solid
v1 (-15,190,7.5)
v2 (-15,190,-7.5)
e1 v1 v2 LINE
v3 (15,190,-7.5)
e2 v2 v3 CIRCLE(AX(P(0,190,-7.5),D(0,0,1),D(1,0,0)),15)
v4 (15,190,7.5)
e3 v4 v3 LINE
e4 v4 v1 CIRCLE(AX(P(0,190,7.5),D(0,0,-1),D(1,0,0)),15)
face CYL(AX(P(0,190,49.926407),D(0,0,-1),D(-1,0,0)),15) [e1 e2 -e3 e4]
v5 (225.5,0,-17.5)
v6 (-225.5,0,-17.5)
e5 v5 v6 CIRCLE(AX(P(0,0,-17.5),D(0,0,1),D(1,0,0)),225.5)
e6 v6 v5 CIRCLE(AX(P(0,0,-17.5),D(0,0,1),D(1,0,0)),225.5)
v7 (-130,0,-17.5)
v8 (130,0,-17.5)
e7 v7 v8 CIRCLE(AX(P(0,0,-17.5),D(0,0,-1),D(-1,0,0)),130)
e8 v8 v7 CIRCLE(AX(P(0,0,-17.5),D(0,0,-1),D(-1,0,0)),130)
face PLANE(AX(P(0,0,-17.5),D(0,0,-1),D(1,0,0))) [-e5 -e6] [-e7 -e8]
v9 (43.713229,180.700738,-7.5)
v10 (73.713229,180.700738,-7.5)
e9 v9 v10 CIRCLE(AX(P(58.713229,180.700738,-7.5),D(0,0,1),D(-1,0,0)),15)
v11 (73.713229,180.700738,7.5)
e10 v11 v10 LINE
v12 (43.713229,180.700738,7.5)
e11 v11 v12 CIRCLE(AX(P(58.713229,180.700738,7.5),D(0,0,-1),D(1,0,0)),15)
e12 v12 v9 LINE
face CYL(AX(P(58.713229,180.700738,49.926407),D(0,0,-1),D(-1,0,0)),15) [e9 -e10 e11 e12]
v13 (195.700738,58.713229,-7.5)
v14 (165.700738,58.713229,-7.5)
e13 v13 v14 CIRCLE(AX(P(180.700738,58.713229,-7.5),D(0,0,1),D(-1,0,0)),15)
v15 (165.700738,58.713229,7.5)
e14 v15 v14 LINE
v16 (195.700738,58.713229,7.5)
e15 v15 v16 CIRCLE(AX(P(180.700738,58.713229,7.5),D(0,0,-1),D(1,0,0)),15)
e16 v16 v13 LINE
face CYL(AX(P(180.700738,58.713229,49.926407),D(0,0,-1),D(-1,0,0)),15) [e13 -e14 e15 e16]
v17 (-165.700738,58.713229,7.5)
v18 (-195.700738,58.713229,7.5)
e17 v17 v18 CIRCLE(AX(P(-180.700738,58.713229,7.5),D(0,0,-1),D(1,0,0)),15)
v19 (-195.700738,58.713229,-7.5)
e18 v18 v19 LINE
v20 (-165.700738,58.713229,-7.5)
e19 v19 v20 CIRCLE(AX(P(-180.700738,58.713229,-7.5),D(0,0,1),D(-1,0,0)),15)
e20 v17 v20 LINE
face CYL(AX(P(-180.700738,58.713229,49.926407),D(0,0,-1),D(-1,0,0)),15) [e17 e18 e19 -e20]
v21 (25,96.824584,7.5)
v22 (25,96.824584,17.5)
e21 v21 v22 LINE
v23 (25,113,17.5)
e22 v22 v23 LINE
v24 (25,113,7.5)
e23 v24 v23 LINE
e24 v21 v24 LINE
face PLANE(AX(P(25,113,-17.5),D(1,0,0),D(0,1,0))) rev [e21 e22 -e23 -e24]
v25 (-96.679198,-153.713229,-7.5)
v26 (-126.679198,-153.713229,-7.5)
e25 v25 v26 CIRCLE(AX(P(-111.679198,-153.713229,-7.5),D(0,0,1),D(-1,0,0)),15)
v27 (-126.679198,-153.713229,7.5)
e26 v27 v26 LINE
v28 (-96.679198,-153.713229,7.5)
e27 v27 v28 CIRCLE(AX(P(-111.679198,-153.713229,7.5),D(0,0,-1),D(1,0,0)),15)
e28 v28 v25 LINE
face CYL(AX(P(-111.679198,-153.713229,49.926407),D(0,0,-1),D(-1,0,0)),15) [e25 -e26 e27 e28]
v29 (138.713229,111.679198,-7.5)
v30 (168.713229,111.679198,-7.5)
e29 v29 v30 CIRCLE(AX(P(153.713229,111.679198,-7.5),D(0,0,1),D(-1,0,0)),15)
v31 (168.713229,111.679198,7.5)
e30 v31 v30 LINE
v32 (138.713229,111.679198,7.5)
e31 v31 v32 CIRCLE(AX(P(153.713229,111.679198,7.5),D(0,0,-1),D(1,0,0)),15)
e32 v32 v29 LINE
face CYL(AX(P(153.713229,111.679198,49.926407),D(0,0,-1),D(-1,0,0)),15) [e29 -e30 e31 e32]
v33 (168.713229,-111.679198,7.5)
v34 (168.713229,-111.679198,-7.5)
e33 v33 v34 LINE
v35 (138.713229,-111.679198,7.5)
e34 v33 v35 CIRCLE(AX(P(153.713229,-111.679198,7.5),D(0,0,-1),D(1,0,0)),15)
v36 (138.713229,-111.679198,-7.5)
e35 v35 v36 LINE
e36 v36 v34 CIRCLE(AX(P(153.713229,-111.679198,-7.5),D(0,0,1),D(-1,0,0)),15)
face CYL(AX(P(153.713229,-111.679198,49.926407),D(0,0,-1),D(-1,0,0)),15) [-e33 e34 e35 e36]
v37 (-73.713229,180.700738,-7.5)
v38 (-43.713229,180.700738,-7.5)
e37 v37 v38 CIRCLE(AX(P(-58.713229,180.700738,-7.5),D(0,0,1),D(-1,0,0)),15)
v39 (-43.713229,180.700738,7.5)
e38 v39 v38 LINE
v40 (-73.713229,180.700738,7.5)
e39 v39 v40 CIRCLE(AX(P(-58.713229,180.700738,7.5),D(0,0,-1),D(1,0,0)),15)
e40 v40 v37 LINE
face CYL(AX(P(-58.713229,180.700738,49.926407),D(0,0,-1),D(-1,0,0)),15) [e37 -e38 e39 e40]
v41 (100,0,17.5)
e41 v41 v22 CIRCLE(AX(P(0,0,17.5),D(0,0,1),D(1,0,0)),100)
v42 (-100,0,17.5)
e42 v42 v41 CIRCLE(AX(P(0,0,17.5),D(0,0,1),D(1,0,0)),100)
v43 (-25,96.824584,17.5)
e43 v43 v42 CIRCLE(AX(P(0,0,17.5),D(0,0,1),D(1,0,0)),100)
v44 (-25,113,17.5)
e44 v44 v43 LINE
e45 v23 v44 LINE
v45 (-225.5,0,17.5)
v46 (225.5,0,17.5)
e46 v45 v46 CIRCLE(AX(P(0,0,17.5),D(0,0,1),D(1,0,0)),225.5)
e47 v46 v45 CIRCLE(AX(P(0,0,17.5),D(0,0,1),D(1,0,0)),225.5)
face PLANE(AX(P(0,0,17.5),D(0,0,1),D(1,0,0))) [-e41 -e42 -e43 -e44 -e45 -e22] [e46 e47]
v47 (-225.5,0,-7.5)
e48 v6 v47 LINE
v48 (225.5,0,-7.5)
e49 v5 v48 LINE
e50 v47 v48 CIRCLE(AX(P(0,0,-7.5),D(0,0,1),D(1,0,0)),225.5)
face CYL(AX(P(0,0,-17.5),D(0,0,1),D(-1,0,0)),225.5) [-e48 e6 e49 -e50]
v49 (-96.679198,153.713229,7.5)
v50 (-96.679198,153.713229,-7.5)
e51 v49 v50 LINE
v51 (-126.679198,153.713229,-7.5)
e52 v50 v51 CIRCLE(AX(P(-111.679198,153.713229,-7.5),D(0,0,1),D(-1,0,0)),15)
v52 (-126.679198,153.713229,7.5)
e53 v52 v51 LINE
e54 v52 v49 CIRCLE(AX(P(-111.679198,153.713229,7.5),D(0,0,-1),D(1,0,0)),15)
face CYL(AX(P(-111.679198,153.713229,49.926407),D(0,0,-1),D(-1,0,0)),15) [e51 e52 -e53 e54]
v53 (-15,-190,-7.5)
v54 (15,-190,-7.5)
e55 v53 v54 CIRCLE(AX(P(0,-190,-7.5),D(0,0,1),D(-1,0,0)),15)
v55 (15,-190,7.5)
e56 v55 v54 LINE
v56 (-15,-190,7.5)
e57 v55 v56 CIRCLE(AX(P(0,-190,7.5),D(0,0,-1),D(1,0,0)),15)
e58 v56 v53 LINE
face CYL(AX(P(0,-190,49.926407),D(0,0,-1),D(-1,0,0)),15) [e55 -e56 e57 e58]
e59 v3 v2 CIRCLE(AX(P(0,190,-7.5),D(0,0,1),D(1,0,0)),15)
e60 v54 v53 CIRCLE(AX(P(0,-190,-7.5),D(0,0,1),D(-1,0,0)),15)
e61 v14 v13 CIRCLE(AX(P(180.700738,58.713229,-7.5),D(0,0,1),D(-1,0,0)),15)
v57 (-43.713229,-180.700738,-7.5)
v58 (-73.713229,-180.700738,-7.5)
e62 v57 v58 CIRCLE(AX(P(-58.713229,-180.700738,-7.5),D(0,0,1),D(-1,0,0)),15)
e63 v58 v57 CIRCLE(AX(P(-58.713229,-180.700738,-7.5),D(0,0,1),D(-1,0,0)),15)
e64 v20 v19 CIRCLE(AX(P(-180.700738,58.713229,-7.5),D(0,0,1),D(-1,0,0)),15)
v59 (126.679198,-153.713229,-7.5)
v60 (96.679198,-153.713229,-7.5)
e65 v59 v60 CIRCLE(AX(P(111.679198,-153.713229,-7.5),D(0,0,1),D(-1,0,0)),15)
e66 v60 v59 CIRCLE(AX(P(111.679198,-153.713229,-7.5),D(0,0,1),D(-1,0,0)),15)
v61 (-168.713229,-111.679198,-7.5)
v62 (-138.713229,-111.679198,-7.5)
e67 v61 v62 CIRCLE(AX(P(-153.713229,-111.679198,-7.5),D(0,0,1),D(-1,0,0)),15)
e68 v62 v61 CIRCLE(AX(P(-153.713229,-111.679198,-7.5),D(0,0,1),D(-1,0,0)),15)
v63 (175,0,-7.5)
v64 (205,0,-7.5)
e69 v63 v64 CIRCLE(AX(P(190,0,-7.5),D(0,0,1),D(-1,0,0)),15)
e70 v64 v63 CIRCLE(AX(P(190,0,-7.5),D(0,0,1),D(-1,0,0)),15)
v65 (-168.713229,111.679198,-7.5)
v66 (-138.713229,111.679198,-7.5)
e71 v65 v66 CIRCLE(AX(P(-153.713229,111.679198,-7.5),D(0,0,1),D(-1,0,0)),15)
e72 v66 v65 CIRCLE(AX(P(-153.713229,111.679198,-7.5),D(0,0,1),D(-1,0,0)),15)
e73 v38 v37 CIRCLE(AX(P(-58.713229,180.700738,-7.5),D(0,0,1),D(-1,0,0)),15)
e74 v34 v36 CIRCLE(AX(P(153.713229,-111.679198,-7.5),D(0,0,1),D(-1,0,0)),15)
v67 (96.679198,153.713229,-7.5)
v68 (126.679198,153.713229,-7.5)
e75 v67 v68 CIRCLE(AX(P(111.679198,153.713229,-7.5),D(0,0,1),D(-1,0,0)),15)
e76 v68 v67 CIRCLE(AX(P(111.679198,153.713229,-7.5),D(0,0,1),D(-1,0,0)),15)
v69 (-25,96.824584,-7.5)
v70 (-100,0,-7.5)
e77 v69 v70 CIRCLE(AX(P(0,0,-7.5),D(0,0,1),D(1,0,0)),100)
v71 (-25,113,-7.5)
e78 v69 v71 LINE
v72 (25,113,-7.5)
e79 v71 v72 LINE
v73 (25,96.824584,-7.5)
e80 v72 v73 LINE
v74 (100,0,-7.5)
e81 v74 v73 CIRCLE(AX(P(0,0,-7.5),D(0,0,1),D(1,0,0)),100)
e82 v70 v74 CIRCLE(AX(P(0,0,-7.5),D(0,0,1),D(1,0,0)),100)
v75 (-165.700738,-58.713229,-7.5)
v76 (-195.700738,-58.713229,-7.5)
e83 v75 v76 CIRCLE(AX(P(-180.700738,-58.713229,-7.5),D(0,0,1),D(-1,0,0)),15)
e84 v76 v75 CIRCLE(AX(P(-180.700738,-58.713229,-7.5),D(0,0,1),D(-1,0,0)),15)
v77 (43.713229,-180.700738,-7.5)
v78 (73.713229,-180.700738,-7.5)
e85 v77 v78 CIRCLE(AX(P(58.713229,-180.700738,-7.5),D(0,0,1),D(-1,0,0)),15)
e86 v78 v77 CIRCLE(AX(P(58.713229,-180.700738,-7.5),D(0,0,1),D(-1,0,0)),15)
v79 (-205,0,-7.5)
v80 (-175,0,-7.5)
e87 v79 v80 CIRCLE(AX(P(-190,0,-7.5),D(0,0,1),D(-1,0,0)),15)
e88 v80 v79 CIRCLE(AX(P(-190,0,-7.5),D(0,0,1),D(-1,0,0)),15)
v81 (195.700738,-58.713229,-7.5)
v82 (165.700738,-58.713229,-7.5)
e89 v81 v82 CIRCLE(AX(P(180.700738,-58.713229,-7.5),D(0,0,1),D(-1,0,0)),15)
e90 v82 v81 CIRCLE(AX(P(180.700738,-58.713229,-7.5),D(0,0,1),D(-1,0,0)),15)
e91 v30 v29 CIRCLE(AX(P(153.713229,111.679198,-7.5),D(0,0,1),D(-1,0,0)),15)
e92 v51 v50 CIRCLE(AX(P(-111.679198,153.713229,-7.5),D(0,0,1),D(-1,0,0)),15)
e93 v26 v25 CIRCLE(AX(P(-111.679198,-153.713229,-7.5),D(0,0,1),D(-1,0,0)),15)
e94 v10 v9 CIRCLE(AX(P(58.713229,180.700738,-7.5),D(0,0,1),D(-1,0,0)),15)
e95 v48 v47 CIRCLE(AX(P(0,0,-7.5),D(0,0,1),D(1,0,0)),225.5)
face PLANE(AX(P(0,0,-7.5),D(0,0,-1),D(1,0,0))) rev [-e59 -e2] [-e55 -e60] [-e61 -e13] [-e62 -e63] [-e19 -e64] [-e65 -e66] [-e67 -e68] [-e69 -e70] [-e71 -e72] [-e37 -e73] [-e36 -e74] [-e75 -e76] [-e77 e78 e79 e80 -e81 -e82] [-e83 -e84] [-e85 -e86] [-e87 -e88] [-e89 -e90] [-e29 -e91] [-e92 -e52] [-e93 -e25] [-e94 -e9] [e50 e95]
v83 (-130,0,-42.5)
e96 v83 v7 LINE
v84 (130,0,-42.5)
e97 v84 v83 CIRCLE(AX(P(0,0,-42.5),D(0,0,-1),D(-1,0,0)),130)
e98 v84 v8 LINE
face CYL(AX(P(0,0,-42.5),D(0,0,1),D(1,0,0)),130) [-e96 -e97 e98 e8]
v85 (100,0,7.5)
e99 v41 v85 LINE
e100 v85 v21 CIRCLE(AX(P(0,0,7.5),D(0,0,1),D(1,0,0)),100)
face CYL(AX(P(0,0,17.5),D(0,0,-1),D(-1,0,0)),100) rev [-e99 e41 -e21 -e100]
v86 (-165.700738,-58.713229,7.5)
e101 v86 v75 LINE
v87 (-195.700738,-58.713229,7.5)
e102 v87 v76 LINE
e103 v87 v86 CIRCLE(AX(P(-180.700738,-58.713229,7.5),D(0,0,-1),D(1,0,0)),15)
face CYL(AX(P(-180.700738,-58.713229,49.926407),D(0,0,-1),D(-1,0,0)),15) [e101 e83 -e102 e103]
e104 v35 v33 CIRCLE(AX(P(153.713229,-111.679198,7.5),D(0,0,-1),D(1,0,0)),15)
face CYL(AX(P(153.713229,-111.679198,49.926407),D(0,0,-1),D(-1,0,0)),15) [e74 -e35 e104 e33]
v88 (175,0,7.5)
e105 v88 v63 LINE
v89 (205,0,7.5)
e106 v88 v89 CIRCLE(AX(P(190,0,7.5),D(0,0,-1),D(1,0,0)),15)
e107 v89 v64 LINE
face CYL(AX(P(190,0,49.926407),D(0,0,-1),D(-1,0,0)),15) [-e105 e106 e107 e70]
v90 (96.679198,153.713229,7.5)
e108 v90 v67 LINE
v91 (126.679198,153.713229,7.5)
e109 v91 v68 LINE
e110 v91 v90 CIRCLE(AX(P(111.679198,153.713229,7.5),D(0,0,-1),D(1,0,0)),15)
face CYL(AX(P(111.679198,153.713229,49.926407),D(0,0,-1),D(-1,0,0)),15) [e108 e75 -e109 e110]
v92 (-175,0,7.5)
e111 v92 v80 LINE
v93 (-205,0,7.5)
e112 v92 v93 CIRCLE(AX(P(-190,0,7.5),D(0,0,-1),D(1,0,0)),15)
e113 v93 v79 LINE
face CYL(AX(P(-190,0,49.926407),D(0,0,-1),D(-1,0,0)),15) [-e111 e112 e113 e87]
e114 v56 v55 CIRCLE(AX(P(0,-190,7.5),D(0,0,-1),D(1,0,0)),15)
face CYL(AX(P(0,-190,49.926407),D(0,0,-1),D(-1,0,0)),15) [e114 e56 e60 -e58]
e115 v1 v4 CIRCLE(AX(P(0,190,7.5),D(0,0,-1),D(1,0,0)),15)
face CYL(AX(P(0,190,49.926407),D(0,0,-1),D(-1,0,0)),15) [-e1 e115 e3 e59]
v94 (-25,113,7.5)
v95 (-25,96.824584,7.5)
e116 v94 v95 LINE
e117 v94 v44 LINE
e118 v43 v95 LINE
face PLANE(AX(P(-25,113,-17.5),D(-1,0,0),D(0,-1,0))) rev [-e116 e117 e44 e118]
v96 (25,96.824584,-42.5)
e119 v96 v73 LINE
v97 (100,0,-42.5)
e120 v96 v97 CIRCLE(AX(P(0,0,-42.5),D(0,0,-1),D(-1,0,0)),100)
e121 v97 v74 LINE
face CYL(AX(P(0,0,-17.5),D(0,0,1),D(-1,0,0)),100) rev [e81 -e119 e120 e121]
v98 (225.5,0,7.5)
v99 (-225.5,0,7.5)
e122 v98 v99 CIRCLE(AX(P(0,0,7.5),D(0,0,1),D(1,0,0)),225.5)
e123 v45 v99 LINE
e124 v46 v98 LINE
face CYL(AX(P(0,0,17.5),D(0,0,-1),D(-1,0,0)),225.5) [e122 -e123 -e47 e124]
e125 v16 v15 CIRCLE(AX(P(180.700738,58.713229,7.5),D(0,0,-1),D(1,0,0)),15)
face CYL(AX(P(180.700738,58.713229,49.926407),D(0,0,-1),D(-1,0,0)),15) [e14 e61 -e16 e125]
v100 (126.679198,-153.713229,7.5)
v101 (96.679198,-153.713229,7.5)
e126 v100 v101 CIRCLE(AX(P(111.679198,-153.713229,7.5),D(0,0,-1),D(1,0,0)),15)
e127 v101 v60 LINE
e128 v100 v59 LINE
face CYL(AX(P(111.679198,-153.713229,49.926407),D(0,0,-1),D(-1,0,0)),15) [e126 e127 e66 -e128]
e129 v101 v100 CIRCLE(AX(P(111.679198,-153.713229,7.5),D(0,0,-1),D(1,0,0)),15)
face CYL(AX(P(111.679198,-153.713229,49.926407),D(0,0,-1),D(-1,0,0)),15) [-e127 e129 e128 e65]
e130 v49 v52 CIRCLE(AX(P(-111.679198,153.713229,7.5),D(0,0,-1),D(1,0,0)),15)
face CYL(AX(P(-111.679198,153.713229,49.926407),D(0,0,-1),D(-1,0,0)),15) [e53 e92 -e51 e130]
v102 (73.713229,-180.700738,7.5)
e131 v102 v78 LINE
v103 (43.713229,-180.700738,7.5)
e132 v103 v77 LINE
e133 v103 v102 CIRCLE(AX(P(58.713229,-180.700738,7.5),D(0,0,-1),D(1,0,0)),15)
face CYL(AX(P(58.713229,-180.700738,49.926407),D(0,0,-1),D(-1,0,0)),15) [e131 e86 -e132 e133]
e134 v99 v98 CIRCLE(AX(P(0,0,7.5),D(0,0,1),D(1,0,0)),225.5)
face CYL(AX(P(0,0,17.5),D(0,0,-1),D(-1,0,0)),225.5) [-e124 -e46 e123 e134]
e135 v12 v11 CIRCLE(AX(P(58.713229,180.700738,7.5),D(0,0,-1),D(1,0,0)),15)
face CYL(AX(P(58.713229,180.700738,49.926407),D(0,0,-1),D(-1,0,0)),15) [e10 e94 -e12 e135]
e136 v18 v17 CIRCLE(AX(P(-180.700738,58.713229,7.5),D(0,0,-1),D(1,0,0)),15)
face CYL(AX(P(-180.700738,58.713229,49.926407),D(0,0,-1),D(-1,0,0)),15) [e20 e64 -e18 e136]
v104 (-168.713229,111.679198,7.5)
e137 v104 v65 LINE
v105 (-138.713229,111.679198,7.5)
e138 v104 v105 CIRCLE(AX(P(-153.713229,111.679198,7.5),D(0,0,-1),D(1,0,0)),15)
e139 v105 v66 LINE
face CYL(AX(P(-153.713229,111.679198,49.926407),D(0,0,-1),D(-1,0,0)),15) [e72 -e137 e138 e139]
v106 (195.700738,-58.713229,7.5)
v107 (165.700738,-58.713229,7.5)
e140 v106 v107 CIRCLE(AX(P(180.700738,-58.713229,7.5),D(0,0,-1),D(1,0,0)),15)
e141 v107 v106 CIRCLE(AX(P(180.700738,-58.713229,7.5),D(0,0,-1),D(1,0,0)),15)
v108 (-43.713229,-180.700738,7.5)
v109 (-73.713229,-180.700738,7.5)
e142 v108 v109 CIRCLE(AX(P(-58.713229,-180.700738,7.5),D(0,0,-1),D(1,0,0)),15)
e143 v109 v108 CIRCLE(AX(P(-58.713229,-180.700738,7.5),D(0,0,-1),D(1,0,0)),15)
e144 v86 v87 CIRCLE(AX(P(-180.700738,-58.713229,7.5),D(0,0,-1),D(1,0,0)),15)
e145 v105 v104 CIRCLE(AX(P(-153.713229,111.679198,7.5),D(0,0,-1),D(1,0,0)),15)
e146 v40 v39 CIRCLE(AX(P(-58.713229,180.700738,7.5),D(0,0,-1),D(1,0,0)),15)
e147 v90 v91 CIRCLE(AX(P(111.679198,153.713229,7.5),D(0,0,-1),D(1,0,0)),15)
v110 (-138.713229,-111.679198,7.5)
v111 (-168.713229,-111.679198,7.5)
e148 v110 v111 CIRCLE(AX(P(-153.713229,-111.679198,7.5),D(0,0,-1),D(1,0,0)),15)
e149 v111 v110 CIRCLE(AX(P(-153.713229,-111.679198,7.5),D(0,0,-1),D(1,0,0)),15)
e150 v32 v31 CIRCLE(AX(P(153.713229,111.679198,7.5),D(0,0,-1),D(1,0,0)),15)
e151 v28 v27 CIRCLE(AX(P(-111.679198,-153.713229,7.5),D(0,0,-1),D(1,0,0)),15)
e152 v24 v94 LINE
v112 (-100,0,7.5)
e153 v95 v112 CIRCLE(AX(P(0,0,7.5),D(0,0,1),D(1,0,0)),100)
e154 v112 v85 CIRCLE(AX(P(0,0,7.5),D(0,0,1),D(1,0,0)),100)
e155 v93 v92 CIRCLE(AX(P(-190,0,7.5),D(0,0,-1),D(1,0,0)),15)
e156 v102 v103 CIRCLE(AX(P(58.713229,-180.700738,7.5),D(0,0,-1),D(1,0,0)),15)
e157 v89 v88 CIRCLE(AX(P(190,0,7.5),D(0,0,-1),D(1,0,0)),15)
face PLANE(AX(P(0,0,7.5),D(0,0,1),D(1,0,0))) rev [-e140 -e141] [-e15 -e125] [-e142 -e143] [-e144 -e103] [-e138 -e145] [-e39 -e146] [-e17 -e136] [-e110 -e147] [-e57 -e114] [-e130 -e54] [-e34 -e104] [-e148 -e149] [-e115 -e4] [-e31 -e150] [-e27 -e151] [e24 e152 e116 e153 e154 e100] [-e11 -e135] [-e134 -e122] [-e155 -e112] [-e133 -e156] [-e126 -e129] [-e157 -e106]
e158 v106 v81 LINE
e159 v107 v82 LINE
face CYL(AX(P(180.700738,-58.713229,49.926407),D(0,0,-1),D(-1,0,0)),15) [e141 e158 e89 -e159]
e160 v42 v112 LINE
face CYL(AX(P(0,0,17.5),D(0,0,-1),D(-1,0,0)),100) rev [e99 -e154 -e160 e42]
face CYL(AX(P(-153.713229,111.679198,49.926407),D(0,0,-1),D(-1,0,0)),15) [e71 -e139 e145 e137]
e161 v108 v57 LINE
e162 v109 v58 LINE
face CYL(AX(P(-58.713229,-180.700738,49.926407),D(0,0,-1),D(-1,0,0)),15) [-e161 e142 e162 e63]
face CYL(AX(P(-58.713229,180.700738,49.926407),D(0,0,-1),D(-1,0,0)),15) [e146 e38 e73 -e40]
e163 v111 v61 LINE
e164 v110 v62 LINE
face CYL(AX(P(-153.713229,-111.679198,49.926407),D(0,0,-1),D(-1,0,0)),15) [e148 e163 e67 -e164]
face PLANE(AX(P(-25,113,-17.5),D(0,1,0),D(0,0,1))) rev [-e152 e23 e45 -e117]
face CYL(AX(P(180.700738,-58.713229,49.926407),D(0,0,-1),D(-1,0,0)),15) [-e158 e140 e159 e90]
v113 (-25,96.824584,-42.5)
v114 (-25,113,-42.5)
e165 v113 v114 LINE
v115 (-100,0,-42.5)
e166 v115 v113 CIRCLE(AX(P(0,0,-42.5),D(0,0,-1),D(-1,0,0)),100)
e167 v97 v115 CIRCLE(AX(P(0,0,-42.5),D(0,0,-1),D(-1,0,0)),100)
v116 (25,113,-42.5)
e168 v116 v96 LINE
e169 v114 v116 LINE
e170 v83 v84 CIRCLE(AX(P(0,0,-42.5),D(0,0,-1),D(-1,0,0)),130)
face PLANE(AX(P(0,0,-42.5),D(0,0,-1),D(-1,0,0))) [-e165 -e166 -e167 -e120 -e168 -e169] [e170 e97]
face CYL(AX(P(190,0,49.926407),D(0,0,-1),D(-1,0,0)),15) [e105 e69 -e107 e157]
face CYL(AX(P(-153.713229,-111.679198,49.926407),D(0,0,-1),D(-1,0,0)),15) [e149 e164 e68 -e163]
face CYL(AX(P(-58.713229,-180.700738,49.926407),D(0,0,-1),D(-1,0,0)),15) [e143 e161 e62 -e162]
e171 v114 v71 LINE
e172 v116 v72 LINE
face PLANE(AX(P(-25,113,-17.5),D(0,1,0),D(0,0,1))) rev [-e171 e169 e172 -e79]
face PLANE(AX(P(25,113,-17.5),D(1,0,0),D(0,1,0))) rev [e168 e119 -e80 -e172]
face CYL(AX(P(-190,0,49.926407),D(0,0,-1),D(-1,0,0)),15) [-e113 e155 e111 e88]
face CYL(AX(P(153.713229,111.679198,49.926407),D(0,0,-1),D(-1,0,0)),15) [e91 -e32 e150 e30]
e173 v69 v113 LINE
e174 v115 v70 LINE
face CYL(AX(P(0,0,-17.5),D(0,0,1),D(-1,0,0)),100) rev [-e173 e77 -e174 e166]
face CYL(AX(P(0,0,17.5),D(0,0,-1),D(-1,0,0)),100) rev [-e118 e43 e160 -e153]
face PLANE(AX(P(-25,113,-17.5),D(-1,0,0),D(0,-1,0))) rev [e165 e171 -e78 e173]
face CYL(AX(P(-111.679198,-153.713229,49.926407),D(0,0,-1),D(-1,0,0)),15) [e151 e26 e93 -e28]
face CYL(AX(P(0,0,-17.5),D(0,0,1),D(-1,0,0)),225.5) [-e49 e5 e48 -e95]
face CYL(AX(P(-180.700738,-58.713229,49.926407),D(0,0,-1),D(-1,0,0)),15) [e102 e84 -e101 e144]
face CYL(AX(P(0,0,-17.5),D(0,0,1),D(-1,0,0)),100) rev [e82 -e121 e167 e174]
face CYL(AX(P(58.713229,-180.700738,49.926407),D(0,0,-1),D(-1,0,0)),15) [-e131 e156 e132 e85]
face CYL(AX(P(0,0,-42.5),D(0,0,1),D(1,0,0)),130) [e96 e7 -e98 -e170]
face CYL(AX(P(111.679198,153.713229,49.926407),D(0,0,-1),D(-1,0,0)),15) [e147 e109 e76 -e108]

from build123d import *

# Parameters (mm, degrees)
BOSS_EXTRUDE1_START = 7.5
SKETCH1_R           = 225.5
SKETCH1_R_2         = 100
BOSS_EXTRUDE1_DEPTH = 10
SKETCH2_R           = 15
BOSS_EXTRUDE2_DEPTH = 15
SKETCH3_W           = 50
SKETCH3_H           = 48.595629982
CUT_EXTRUDE1_DEPTH  = 321.820043015
SKETCH4_R           = 130
BOSS_EXTRUDE3_DEPTH = 25


with BuildPart() as part:
    # Sketch1 → Boss-Extrude1 (new body)
    with BuildSketch(Plane.XY.offset(BOSS_EXTRUDE1_START)):
        Circle(SKETCH1_R)
        Circle(SKETCH1_R_2, mode=Mode.SUBTRACT)
    extrude(amount=BOSS_EXTRUDE1_DEPTH)


with BuildPart() as body_2:
    # Mirror1: mirrored copy
    add(part.part.mirror(Plane.XY))


with BuildPart() as part_1:
    add(part.part)

    add(body_2.part)  # Boss-Extrude2 merges body 2
    # Sketch2 → Boss-Extrude2 (add)
    with BuildSketch(Plane.XY.offset(-7.5)):
        with Locations((0, 190)):
            Circle(SKETCH2_R)
        with Locations(Location((58.713228931, 180.700738096, 0), (0, 0, 180))):
            Circle(SKETCH2_R)
        with Locations(Location((111.679197936, 153.713228931, 0), (0, 0, 180))):
            Circle(SKETCH2_R)
        with Locations(Location((153.713228931, 111.679197936, 0), (0, 0, 180))):
            Circle(SKETCH2_R)
        with Locations(Location((180.700738096, 58.713228931, 0), (0, 0, 180))):
            Circle(SKETCH2_R)
        with Locations(Location((190, 0, 0), (0, 0, 180))):
            Circle(SKETCH2_R)
        with Locations(Location((180.700738096, -58.713228931, 0), (0, 0, 180))):
            Circle(SKETCH2_R)
        with Locations(Location((153.713228931, -111.679197936, 0), (0, 0, 180))):
            Circle(SKETCH2_R)
        with Locations(Location((111.679197936, -153.713228931, 0), (0, 0, 180))):
            Circle(SKETCH2_R)
        with Locations(Location((58.713228931, -180.700738096, 0), (0, 0, 180))):
            Circle(SKETCH2_R)
        with Locations(Location((0, -190, 0), (0, 0, 180))):
            Circle(SKETCH2_R)
        with Locations(Location((-58.713228931, -180.700738096, 0), (0, 0, 180))):
            Circle(SKETCH2_R)
        with Locations(Location((-111.679197936, -153.713228931, 0), (0, 0, 180))):
            Circle(SKETCH2_R)
        with Locations(Location((-153.713228931, -111.679197936, 0), (0, 0, 180))):
            Circle(SKETCH2_R)
        with Locations(Location((-180.700738096, -58.713228931, 0), (0, 0, 180))):
            Circle(SKETCH2_R)
        with Locations(Location((-190, 0, 0), (0, 0, 180))):
            Circle(SKETCH2_R)
        with Locations(Location((-180.700738096, 58.713228931, 0), (0, 0, 180))):
            Circle(SKETCH2_R)
        with Locations(Location((-153.713228931, 111.679197936, 0), (0, 0, 180))):
            Circle(SKETCH2_R)
        with Locations(Location((-111.679197936, 153.713228931, 0), (0, 0, 180))):
            Circle(SKETCH2_R)
        with Locations(Location((-58.713228931, 180.700738096, 0), (0, 0, 180))):
            Circle(SKETCH2_R)
    extrude(amount=BOSS_EXTRUDE2_DEPTH)

    # Sketch3 → Cut-Extrude1 (cut, through all)
    with BuildSketch(Plane.XY.offset(17.5)):
        with Locations((0, 88.702185009)):
            Rectangle(SKETCH3_W, SKETCH3_H)
    extrude(amount=-CUT_EXTRUDE1_DEPTH, mode=Mode.SUBTRACT)

    # Sketch4 → Boss-Extrude3 (add)
    with BuildSketch(Plane(origin=(0, 0, -17.5), x_dir=(-1, 0, 0), z_dir=(0, 0, -1))):
        Circle(SKETCH4_R)
        with BuildLine():
            Line((-25, 113), (25, 113))
            Line((25, 113), (25, 96.824583655))
            ThreePointArc((25, 96.824583655), (0, -100), (-25, 96.824583655))
            Line((-25, 96.824583655), (-25, 113))
        make_face(mode=Mode.SUBTRACT)
    extrude(amount=BOSS_EXTRUDE3_DEPTH)


solid = part_1.part
